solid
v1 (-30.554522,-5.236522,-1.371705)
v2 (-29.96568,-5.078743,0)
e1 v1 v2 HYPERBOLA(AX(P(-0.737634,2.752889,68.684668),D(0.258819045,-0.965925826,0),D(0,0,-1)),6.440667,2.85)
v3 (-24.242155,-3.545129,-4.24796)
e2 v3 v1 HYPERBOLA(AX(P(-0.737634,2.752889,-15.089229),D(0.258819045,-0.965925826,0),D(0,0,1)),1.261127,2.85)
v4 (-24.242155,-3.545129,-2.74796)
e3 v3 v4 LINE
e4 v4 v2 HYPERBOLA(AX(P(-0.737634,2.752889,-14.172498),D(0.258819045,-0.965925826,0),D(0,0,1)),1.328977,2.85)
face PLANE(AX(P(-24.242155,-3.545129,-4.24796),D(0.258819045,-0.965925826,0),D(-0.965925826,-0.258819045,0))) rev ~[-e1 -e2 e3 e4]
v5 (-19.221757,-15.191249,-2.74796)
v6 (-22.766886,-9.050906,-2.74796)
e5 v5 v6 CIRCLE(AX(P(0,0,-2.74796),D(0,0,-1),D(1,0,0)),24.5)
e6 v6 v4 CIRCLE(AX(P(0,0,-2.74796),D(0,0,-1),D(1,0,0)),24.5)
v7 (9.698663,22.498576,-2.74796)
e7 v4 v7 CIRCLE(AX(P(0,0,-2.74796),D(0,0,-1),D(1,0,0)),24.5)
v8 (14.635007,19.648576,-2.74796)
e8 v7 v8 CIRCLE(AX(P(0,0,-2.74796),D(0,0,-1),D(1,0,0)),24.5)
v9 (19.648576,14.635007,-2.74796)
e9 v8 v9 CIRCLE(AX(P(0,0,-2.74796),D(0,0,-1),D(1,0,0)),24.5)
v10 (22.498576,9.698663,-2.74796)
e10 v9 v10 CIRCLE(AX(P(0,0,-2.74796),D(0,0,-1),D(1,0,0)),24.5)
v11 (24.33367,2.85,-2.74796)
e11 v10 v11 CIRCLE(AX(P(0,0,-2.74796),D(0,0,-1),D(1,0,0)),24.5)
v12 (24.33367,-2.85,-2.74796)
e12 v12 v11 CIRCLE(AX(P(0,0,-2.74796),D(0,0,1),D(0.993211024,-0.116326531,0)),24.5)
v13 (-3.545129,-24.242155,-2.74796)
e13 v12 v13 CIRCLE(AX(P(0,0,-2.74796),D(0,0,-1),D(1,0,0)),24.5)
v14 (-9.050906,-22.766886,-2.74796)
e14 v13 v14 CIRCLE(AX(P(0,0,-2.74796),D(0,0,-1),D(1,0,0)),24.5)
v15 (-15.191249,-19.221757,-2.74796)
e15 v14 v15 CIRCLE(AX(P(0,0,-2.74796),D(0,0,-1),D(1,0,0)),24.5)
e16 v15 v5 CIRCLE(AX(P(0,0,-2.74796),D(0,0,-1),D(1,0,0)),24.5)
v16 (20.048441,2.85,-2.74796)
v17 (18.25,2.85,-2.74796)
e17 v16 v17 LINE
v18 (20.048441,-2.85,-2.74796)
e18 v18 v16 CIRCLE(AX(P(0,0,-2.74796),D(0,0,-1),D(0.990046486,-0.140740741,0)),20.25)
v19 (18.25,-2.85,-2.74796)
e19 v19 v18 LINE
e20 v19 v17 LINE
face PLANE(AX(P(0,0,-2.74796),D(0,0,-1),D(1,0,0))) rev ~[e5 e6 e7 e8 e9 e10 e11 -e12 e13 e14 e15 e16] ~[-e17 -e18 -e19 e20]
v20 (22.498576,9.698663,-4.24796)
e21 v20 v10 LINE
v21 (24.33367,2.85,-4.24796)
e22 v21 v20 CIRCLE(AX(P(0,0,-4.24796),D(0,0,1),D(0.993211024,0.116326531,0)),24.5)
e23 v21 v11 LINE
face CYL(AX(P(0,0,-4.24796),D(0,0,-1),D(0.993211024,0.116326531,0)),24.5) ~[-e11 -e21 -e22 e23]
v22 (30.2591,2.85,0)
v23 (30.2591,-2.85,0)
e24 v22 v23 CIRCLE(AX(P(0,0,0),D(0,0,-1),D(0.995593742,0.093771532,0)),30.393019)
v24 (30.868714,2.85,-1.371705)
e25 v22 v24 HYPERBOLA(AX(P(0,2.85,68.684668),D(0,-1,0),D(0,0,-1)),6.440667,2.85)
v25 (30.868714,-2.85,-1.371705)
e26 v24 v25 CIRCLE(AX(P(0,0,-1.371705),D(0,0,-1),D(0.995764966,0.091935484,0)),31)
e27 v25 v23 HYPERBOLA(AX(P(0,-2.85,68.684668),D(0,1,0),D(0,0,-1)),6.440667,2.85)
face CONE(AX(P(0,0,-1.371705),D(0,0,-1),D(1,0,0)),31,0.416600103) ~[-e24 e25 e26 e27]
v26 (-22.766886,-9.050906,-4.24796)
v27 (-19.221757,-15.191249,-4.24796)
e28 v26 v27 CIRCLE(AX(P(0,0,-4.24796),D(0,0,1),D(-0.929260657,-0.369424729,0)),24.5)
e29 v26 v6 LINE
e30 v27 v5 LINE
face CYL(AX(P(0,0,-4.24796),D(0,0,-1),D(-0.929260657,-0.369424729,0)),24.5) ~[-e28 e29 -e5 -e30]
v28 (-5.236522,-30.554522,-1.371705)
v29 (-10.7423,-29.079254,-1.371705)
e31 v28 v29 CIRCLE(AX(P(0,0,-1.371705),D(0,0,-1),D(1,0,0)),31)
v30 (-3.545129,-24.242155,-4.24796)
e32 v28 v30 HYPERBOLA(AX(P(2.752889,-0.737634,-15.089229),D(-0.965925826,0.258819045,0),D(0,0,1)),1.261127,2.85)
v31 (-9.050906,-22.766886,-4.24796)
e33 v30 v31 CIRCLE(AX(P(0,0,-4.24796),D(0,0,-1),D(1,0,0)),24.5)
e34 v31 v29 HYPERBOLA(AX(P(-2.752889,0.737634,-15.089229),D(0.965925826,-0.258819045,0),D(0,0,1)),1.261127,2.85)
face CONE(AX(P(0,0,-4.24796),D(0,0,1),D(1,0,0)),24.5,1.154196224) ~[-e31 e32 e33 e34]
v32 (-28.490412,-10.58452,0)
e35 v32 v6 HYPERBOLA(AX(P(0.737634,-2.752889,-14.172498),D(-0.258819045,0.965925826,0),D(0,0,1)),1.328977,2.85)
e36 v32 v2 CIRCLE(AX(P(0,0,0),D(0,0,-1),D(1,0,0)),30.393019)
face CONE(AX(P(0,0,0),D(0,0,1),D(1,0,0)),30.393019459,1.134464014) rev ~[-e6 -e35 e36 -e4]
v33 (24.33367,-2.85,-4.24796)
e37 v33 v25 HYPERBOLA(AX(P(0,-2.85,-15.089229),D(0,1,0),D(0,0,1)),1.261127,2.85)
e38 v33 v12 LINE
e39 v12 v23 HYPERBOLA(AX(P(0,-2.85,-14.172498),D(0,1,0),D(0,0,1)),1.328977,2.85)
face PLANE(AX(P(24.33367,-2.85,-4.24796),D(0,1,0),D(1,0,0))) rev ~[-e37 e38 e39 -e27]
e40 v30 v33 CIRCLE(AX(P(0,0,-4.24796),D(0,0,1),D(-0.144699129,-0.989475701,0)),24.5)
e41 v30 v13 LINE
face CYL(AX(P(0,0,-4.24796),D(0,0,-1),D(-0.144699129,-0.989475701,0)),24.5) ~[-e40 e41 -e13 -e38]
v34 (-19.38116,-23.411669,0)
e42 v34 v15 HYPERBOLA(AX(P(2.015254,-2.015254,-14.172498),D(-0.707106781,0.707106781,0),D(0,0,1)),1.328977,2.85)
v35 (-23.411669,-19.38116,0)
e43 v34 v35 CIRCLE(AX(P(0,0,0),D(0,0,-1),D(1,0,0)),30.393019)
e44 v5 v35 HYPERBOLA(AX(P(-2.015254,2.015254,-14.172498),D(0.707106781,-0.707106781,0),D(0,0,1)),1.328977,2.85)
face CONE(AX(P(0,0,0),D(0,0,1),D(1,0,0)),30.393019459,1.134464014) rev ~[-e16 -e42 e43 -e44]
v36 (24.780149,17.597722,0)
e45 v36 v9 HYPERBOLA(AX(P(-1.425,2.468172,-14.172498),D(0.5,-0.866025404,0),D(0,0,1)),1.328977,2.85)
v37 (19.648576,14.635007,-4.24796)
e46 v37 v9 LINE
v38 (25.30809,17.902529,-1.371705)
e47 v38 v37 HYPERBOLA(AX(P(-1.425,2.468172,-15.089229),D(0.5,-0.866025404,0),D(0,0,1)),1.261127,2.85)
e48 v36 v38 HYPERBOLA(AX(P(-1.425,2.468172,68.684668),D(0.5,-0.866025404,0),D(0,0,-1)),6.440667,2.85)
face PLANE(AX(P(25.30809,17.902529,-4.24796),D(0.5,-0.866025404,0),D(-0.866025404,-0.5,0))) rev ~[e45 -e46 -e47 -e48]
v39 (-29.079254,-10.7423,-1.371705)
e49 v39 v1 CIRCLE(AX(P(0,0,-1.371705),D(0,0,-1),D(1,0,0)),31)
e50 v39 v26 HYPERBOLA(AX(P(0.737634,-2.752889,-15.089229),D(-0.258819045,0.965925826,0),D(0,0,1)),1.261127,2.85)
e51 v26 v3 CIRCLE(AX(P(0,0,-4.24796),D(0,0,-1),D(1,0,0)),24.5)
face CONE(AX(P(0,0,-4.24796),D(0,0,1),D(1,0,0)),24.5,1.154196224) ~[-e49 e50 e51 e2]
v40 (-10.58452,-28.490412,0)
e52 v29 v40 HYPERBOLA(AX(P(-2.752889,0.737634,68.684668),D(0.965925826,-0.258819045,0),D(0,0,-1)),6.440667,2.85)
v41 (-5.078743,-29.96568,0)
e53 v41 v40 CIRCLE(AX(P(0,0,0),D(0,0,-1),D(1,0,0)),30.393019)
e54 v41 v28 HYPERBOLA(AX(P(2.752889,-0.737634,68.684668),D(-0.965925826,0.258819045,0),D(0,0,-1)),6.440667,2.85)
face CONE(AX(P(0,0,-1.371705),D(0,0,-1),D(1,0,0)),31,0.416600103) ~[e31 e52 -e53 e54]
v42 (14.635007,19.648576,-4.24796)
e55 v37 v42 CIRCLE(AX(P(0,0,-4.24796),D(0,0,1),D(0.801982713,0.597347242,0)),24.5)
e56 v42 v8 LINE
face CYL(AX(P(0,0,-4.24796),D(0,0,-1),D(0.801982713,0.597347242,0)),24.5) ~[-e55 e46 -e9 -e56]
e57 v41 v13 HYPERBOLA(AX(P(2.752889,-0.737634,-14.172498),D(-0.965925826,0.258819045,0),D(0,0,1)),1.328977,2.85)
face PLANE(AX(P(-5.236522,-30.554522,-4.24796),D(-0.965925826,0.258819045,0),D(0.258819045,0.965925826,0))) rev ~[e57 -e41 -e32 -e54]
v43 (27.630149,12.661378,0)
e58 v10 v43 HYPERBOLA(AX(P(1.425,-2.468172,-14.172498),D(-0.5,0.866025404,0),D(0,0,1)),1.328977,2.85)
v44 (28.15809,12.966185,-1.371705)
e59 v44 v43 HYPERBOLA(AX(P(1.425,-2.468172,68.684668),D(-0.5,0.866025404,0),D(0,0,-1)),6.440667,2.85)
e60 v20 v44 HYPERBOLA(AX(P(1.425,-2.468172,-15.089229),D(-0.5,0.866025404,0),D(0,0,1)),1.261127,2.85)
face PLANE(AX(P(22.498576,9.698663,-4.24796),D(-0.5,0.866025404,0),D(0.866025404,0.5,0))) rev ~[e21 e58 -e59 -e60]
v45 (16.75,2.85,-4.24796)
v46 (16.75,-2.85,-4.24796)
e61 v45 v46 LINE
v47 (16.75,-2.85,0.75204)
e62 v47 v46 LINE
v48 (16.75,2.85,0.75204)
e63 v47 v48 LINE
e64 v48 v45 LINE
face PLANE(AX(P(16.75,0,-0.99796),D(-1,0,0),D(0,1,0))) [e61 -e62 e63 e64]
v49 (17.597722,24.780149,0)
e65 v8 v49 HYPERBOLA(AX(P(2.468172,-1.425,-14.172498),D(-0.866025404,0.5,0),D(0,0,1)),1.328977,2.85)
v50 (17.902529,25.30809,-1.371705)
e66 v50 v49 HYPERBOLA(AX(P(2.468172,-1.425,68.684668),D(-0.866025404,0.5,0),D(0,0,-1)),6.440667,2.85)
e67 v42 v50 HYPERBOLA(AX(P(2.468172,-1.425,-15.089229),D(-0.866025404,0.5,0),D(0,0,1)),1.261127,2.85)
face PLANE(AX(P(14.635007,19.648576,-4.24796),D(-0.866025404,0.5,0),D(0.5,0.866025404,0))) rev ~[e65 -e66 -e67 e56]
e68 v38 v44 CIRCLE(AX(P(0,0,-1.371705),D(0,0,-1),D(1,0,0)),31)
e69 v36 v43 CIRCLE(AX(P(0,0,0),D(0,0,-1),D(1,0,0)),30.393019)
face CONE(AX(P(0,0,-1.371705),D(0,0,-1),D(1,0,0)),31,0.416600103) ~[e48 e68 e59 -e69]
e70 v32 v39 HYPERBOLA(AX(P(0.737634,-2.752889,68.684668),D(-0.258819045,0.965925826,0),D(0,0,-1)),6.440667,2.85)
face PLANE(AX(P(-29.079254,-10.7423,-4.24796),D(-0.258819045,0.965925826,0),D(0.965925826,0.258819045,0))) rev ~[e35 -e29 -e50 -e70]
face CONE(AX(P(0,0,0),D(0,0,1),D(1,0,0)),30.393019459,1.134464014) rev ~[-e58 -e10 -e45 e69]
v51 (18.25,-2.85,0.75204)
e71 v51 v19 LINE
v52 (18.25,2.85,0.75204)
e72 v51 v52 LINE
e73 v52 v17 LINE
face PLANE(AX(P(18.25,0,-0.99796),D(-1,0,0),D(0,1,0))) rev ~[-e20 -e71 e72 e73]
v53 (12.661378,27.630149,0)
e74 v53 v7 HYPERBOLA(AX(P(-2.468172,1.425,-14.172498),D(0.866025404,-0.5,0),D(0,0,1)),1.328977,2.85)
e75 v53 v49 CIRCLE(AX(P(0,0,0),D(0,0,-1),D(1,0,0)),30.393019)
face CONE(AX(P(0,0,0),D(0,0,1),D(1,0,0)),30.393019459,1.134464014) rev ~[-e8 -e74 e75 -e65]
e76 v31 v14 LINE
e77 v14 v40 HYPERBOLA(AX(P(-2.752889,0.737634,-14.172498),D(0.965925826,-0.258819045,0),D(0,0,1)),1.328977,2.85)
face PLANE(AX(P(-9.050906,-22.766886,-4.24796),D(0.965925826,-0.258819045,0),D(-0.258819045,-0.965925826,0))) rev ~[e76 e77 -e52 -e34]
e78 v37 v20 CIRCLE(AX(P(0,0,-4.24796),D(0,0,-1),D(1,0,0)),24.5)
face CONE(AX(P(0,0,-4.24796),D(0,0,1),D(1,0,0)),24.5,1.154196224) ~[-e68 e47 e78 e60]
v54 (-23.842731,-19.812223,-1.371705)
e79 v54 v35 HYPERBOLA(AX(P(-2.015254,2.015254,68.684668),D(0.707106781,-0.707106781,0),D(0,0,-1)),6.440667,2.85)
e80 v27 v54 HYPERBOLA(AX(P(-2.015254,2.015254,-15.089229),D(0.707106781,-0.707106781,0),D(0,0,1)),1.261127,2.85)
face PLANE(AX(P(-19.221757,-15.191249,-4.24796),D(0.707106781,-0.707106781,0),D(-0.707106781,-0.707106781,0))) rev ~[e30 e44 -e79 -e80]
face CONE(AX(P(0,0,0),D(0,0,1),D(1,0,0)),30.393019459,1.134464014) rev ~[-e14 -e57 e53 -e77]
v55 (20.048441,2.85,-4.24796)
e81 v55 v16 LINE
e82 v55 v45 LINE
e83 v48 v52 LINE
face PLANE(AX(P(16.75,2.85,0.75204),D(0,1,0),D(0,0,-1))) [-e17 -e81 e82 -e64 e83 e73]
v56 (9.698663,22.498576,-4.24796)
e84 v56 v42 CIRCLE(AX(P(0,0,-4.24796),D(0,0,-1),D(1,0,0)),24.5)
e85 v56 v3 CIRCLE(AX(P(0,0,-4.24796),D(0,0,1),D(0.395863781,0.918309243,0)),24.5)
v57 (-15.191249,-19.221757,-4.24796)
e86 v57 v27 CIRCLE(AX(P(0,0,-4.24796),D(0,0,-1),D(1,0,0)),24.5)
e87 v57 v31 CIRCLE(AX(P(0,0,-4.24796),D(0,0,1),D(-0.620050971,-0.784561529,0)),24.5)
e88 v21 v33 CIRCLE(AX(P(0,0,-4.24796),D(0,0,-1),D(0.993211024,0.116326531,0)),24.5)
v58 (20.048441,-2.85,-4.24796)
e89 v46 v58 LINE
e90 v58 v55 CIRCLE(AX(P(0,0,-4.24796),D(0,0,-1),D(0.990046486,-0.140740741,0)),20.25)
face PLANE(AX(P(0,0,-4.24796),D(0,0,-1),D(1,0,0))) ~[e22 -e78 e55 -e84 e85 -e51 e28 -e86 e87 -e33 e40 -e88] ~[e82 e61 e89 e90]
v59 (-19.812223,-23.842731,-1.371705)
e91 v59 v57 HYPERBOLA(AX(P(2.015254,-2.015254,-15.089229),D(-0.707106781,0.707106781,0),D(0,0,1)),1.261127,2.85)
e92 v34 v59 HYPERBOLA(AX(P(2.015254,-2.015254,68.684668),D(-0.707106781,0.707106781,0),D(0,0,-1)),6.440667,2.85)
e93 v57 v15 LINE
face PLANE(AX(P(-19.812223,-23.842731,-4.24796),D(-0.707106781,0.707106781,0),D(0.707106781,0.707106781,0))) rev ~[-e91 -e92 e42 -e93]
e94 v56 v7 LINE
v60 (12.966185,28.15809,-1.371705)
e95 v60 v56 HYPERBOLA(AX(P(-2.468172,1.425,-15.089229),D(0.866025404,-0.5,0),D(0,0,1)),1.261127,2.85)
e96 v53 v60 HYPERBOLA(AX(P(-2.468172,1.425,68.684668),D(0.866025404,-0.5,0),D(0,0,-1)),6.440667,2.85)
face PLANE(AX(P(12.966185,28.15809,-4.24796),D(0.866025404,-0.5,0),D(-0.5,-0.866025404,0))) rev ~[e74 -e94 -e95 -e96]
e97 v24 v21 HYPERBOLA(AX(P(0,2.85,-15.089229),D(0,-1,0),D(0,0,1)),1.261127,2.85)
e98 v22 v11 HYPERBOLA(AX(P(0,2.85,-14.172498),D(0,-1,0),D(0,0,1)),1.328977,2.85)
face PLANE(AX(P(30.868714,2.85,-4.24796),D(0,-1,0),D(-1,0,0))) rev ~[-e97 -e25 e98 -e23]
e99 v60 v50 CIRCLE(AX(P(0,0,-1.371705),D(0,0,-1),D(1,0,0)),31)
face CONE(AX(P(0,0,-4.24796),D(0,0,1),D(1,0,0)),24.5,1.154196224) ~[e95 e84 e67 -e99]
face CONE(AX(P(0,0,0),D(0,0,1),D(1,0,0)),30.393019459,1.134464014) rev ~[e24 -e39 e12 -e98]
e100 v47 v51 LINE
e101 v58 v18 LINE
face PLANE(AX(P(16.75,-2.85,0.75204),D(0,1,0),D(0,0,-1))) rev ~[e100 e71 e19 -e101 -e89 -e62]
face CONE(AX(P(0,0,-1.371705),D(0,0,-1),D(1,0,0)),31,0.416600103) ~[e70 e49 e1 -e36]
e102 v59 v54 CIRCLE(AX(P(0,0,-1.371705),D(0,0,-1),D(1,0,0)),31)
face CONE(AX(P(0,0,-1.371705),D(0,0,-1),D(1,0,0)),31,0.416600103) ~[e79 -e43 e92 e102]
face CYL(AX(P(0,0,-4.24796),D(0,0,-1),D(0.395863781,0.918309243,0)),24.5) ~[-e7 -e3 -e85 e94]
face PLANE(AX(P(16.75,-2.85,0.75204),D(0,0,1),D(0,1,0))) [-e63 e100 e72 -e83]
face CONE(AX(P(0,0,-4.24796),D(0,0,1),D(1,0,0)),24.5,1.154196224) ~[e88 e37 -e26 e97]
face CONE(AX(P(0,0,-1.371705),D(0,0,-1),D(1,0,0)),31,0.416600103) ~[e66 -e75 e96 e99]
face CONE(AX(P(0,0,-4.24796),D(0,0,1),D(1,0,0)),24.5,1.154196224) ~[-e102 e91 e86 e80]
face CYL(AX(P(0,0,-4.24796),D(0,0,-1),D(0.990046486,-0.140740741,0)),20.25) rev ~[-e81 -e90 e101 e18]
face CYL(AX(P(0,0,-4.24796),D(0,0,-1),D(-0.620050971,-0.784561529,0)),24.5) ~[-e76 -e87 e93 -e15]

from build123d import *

# Parameters (mm, degrees)
SKETCH2_OUTSIDE_W = 81.556
SKETCH2_OUTSIDE_H = 81.556
CUT_EXTRUDE_DEPTH = 47.45561719
SKETCH4_W         = 5.7
SKETCH4_H         = 3.5
EXTRUDE1_DEPTH    = 1.5


with BuildPart() as part:
    # Sketch1 → Base-Extrude (revolve)
    with BuildSketch(Plane.YZ, mode=Mode.PRIVATE) as base_extrude_sk:
        Polygon((0, -4.247960103), (-24.5, -4.247960103), (-31, -1.371705006), (-30.393019459, 0), (-24.5, -2.747960103), (0, -2.747960103), align=None)
    revolve(base_extrude_sk.sketch.rotate(Axis((0, 0, 5.823648763), (0, 0, -1)), 270), axis=Axis((0, 0, 5.823648763), (0, 0, -1)))

    # Sketch2 outside → Cut-Extrude (cut, through all)
    # profile 1 of 2: a face of its own
    with BuildSketch(Plane(origin=(-2.40435344, 1.003568156, -4.247960103), x_dir=(-1, 0, 0), z_dir=(0, 0, -1))):
        with Locations((-2.404, -1.004)):
            Rectangle(SKETCH2_OUTSIDE_W, SKETCH2_OUTSIDE_H)
        with BuildLine():
            Line((-26.738023529, -3.853568156), (-33.273067375, -3.853568156))
            ThreePointArc((-33.273067375, -3.853568156), (-33.40435344, -1.003568156), (-33.273067375, 1.846431844))
            Line((-33.273067375, 1.846431844), (-26.738023529, 1.846431844))
            ThreePointArc((-26.738023529, 1.846431844), (-26.069536184, 5.337498449), (-24.902929904, 8.695094487))
            Line((-24.902929904, 8.695094487), (-30.562443889, 11.96261641))
            ThreePointArc((-30.562443889, 11.96261641), (-29.251140957, 14.496431844), (-27.712443889, 16.898961212))
            Line((-27.712443889, 16.898961212), (-22.052929904, 13.631439289))
            ThreePointArc((-22.052929904, 13.631439289), (-19.728469579, 16.320547983), (-17.039360885, 18.645008308))
            Line((-17.039360885, 18.645008308), (-20.306882808, 24.304522293))
            ThreePointArc((-20.306882808, 24.304522293), (-17.90435344, 25.843219361), (-15.370538006, 27.154522293))
            Line((-15.370538006, 27.154522293), (-12.103016083, 21.495008308))
            ThreePointArc((-12.103016083, 21.495008308), (12.510301571, 18.433588681), (21.837801226, -4.548696808))
            Line((21.837801226, -4.548696808), (28.150168853, -6.240090616))
            ThreePointArc((28.150168853, -6.240090616), (27.539347175, -9.026958555), (26.674900296, -11.745867825))
            Line((26.674900296, -11.745867825), (20.362532669, -10.054474018))
            ThreePointArc((20.362532669, -10.054474018), (18.813268953, -13.253568156), (16.817404018, -16.194816961))
            Line((16.817404018, -16.194816961), (21.438377837, -20.81579078))
            ThreePointArc((21.438377837, -20.81579078), (19.515956777, -22.923878373), (17.407869184, -24.846299433))
            Line((17.407869184, -24.846299433), (12.786895365, -20.225325614))
            ThreePointArc((12.786895365, -20.225325614), (9.84564656, -22.221190549), (6.646552422, -23.770454265))
            Line((6.646552422, -23.770454265), (8.33794623, -30.082821892))
            ThreePointArc((8.33794623, -30.082821892), (5.619036959, -30.947268771), (2.83216902, -31.558090449))
            Line((2.83216902, -31.558090449), (1.140775212, -25.245722822))
            ThreePointArc((1.140775212, -25.245722822), (-17.31900845, -20.440724994), (-26.738023529, -3.853568156))
        make_face(mode=Mode.SUBTRACT)
    # profile 2 of 2: a face of its own
    with BuildSketch(Plane(origin=(-2.40435344, 1.003568156, -4.247960103), x_dir=(-1, 0, 0), z_dir=(0, 0, -1))):
        with BuildLine():
            Line((-22.452794776, 1.846431844), (-19.15435344, 1.846431844))
            Line((-19.15435344, 1.846431844), (-19.15435344, -3.853568156))
            Line((-19.15435344, -3.853568156), (-22.452794776, -3.853568156))
            ThreePointArc((-22.452794776, -3.853568156), (17.84564656, -1.003568156), (-22.452794776, 1.846431844))
        make_face()
    extrude(amount=-CUT_EXTRUDE_DEPTH, mode=Mode.SUBTRACT)

    # Sketch4 → Extrude1 (add)
    with BuildSketch(Plane(origin=(16.75, -0.667304961, -0.255028377), x_dir=(0, 1, 0), z_dir=(-1, 0, 0))):
        with Locations((0.667304961, 0.742931726)):
            Rectangle(SKETCH4_W, SKETCH4_H)
    extrude(amount=-EXTRUDE1_DEPTH)


solid = part.part
